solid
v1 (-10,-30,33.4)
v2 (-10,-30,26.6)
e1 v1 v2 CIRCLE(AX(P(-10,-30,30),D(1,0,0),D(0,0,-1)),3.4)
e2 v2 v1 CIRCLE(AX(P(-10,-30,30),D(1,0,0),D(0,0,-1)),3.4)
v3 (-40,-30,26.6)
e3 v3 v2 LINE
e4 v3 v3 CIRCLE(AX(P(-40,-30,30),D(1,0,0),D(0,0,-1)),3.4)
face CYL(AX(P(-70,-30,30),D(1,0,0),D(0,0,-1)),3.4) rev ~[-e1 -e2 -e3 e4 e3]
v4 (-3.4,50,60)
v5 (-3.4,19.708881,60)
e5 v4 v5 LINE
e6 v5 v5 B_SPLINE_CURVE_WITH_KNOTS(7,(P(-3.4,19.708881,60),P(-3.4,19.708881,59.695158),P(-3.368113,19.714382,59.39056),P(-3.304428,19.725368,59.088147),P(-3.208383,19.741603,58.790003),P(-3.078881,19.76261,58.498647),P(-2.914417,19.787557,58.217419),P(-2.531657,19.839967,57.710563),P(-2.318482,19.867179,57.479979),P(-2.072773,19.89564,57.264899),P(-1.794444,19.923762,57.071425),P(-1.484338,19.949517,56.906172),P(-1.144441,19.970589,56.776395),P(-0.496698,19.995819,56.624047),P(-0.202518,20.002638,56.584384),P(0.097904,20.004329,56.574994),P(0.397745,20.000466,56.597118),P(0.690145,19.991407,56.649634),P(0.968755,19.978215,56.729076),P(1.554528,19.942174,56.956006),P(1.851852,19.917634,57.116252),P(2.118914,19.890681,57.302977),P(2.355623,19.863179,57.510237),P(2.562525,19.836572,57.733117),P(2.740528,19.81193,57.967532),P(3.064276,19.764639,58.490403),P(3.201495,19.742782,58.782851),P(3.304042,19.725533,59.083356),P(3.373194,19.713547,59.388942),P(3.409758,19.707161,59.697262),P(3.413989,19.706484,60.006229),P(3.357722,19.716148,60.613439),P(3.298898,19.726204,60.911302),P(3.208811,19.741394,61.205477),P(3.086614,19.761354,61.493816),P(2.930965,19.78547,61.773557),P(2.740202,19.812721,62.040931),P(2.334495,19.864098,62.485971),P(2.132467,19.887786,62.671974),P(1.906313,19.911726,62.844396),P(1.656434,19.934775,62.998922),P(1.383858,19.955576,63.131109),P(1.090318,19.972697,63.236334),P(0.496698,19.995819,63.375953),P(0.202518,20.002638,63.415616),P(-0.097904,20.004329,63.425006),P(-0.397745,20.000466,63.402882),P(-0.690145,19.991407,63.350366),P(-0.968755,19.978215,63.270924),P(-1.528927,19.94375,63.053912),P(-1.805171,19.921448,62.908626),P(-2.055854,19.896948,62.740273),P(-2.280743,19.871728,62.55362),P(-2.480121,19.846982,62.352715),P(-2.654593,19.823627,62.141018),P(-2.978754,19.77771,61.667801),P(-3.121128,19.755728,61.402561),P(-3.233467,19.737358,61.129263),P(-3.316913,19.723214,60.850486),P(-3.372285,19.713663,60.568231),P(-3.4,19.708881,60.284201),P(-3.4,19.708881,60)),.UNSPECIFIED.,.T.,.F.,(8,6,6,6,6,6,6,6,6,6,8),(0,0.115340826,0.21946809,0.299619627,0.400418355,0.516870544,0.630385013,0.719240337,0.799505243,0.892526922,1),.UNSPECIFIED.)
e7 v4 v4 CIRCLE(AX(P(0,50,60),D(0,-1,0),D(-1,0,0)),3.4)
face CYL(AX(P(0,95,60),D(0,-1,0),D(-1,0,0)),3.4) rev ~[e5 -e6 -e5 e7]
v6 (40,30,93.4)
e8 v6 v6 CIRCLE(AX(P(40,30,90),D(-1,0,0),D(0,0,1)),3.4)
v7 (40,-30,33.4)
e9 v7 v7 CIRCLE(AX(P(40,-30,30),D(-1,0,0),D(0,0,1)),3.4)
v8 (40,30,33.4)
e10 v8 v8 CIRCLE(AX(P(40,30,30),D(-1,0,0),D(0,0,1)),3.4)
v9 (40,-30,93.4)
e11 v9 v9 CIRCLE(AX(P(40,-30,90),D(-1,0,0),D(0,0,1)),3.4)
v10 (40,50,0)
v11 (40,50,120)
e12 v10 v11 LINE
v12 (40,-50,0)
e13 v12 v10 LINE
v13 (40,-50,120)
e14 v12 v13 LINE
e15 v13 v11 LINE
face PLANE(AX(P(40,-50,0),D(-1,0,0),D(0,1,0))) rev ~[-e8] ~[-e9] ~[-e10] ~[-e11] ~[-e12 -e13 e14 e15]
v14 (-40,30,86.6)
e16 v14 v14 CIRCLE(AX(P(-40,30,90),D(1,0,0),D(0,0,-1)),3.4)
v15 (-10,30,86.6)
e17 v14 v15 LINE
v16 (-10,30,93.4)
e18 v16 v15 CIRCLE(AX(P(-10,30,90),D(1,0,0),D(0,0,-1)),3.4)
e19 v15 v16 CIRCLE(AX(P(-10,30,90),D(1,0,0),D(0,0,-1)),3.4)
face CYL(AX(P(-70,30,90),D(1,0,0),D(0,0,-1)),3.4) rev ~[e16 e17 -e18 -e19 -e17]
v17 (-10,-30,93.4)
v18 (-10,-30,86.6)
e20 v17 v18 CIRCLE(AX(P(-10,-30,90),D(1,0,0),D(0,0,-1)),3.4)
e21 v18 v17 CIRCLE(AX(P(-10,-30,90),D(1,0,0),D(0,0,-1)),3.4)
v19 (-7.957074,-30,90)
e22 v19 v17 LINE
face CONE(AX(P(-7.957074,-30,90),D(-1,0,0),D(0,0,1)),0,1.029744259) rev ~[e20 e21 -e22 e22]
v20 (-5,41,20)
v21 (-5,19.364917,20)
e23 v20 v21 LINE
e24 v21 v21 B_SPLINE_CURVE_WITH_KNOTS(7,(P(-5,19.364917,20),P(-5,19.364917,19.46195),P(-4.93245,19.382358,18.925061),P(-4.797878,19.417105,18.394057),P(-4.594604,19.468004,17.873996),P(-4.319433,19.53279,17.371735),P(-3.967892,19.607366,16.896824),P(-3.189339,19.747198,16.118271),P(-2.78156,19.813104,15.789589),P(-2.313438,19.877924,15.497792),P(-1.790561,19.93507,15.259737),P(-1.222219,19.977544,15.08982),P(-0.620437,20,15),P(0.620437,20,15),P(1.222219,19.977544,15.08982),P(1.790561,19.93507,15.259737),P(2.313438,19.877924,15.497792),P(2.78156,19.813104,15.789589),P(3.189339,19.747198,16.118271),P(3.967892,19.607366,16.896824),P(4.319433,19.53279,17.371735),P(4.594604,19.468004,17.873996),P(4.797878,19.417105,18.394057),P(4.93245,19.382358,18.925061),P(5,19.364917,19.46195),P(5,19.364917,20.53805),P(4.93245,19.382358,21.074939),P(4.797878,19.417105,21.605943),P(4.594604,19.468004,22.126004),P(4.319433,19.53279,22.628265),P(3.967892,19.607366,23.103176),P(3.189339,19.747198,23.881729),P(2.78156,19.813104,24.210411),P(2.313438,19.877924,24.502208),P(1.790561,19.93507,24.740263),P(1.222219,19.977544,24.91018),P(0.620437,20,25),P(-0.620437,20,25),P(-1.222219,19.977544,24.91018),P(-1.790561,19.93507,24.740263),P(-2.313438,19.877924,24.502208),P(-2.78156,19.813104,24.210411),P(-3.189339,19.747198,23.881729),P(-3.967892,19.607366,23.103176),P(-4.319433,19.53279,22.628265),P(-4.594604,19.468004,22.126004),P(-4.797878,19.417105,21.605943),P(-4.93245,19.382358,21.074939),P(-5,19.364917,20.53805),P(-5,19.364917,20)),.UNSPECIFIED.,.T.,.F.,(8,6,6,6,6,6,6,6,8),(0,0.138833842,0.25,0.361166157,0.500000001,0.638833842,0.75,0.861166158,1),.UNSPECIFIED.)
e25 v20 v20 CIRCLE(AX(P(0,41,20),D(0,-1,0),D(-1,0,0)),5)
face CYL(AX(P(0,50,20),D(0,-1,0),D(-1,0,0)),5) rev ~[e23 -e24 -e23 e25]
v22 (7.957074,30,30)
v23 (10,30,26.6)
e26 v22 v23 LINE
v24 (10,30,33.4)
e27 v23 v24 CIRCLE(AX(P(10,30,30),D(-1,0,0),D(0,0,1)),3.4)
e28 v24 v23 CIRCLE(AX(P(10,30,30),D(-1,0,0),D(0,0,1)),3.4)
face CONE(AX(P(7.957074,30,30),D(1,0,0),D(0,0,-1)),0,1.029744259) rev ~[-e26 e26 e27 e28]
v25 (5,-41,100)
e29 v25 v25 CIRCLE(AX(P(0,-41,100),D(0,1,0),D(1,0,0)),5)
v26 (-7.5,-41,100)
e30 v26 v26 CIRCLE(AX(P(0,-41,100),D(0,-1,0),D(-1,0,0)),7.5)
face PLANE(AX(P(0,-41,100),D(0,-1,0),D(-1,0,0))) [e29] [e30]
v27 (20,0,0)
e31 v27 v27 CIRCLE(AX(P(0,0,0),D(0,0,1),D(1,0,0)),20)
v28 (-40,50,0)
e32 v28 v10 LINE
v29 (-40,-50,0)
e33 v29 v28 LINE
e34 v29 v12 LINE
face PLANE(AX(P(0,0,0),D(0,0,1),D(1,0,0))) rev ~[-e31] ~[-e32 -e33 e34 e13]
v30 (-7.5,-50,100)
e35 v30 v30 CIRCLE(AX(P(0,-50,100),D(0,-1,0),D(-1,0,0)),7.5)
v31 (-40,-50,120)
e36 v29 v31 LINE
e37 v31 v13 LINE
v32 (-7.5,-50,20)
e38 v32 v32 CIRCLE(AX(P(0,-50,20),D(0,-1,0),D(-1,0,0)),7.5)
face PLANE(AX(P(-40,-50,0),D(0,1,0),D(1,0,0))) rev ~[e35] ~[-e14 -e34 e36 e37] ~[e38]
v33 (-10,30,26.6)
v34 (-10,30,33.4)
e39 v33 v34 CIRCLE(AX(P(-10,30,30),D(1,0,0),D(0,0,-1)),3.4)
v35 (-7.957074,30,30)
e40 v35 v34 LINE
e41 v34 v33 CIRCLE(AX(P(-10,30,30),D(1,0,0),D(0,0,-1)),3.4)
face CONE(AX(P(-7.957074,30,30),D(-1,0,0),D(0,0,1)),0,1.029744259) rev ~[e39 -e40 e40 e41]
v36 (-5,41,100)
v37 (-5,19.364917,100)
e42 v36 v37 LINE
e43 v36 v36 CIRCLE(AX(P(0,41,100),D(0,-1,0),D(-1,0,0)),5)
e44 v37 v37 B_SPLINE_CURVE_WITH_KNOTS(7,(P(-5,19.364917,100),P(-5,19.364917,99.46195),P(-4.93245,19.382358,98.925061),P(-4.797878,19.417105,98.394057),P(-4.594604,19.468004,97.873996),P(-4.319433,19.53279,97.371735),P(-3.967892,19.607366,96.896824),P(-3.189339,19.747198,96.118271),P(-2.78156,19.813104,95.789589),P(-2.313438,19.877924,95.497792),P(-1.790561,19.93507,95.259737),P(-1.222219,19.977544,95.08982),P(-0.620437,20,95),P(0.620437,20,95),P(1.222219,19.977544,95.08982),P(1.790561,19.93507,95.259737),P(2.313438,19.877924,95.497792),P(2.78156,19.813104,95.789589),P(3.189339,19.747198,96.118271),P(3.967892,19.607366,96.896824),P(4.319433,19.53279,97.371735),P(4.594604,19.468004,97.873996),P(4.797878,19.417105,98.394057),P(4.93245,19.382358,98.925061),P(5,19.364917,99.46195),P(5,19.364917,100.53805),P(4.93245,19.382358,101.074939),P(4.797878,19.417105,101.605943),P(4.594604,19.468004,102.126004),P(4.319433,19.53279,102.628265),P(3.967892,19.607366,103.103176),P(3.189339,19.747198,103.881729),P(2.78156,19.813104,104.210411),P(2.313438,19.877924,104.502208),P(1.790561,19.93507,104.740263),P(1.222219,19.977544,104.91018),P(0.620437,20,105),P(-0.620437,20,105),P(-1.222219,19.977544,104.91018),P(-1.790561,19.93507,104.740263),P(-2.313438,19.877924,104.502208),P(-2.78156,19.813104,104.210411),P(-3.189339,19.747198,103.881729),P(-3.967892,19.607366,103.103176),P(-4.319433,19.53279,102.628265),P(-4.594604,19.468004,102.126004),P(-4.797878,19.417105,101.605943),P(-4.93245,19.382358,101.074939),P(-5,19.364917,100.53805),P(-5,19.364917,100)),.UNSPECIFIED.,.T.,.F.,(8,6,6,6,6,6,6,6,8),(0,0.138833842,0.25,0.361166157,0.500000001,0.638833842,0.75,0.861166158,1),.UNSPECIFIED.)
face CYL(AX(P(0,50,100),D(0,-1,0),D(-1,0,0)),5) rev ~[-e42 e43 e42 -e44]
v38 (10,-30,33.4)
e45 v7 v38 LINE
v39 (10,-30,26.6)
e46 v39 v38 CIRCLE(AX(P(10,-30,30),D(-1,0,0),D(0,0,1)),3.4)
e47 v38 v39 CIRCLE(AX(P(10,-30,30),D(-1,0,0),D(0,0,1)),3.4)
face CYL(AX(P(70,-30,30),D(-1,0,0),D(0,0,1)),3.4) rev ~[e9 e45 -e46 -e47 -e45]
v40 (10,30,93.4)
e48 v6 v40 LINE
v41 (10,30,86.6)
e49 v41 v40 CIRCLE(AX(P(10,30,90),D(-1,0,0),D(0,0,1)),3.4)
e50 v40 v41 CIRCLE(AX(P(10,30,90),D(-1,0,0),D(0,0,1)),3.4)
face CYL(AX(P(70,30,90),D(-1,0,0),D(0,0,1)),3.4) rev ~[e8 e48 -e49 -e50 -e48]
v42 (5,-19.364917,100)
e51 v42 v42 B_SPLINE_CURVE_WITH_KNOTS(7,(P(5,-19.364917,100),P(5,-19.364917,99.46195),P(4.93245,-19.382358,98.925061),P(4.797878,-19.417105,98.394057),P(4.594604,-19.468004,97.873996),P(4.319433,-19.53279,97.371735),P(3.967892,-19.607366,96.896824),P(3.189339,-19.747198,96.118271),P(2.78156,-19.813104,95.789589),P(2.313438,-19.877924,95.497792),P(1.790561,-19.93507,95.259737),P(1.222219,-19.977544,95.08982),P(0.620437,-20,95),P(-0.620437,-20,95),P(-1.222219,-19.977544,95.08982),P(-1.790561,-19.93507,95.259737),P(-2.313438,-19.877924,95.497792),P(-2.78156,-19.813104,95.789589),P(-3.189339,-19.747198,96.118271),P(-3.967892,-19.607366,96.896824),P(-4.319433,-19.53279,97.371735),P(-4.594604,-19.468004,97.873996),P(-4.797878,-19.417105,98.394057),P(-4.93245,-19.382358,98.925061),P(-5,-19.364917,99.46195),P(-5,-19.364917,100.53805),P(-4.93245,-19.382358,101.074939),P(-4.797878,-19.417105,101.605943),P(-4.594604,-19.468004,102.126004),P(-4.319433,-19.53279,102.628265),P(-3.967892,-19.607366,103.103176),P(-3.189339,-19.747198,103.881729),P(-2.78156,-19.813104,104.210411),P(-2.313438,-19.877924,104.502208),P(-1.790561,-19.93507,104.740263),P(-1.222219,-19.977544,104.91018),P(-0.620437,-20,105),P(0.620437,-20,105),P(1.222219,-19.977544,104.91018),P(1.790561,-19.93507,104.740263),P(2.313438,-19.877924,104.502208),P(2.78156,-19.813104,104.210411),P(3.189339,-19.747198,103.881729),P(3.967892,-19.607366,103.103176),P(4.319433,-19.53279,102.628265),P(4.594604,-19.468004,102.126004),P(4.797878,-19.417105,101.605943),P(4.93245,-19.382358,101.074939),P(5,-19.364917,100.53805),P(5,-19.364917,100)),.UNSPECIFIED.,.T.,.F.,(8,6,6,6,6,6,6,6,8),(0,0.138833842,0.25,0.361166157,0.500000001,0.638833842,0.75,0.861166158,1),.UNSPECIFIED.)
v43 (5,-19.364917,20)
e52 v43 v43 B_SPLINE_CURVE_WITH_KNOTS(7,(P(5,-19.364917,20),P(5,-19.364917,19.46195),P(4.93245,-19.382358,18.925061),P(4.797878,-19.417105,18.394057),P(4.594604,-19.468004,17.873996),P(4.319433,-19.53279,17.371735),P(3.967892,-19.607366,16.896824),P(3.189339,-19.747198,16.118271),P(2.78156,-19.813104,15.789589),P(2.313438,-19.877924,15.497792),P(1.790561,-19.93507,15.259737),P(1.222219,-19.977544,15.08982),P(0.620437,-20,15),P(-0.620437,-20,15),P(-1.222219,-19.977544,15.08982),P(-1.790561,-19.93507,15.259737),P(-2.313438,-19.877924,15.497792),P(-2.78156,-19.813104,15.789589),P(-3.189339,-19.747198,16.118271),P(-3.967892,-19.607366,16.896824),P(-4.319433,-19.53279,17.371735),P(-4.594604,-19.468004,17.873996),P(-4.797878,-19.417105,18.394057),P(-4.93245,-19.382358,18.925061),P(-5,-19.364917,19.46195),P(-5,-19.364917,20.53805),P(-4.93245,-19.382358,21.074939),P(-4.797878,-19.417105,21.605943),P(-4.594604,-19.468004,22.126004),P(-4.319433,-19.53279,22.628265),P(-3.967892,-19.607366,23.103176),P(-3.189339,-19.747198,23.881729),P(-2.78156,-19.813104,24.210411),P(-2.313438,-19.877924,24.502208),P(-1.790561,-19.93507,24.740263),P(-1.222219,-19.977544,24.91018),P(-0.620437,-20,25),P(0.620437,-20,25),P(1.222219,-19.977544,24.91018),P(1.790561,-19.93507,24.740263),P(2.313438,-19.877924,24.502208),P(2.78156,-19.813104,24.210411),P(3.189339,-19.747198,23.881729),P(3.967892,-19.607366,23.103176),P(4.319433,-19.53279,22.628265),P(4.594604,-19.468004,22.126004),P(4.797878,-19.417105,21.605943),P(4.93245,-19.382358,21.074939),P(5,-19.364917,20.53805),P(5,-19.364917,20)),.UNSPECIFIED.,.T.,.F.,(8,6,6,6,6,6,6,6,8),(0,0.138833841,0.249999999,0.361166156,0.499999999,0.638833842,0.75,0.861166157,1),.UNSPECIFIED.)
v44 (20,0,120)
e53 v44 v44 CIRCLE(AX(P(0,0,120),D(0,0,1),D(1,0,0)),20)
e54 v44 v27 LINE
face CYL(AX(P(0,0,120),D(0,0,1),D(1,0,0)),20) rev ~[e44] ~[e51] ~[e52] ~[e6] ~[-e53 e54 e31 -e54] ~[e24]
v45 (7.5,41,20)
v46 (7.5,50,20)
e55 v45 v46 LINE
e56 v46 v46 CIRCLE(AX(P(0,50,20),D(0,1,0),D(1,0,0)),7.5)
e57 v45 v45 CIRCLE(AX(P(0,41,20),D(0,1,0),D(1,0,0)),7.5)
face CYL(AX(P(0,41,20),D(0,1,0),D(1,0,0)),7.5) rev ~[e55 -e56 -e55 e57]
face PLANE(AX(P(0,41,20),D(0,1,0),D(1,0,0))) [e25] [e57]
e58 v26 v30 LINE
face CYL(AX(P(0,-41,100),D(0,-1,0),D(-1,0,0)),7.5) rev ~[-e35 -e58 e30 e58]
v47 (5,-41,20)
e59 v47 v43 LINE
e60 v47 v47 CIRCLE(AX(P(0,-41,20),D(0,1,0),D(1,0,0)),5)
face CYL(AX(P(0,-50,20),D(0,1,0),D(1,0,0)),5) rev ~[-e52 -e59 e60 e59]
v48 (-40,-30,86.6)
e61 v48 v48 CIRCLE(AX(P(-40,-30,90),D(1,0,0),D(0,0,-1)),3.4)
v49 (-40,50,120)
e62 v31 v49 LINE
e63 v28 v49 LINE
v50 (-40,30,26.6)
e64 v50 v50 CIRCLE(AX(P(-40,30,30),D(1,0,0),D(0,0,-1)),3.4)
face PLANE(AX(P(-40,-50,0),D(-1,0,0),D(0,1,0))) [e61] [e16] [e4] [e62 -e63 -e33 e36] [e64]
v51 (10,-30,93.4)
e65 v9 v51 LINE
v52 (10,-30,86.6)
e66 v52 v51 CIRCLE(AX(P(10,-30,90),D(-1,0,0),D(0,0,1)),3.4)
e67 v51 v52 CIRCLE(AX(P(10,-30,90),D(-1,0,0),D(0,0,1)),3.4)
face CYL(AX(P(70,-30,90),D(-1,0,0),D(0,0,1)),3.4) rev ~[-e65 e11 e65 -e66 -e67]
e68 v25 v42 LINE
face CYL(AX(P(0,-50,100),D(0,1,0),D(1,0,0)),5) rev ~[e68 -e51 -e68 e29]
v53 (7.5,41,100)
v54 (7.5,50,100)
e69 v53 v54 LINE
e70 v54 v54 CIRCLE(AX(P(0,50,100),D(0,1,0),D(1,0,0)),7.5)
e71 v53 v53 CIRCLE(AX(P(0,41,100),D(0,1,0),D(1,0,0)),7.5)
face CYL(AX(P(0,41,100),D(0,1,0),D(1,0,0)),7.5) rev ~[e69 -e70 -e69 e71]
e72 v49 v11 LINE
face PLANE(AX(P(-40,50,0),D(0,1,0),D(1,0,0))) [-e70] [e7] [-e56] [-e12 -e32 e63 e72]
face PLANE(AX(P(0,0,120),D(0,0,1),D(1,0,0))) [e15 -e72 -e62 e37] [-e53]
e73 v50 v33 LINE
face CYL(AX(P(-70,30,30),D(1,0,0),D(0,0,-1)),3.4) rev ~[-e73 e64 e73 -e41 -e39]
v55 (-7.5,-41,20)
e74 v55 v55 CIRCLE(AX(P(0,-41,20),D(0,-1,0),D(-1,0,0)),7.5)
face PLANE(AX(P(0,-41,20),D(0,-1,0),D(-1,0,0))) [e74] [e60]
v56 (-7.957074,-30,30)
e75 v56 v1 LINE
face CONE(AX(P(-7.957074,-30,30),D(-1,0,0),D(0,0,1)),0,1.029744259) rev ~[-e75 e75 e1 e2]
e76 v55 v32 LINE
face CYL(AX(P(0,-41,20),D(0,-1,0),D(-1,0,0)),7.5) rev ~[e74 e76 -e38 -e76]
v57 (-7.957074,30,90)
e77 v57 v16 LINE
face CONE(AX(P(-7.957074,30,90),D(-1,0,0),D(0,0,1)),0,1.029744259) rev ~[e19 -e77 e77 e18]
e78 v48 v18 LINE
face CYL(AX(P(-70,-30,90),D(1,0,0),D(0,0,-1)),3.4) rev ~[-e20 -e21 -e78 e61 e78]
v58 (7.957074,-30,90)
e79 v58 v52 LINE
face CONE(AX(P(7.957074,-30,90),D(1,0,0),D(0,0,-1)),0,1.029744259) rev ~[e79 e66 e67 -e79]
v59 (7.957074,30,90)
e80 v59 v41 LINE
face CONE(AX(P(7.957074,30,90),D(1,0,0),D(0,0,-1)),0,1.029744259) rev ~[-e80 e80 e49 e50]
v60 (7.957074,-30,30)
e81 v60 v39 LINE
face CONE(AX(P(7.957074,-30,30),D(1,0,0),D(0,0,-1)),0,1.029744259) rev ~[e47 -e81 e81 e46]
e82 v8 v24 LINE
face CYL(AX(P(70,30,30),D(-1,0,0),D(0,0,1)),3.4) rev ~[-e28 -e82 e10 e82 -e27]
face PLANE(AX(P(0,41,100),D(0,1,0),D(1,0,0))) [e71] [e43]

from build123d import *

# Parameters (mm, degrees)
SKETCH1_W                                          = 80
SKETCH1_H                                          = 100
BOSS_EXTRUDE1_DEPTH                                = 120
SKETCH2_R                                          = 20
CUT_EXTRUDE1_DEPTH                                 = 137.014705087
HOLE_SIZE_BASED_ON_HEX_SOCKET_CAP_SCRE_D           = 10
HOLE_SIZE_BASED_ON_HEX_SOCKET_CAP_SCRE_DEPTH       = 35
HOLE_SIZE_BASED_ON_HEX_SOCKET_CAP_SCRE_CBORE_D     = 15
HOLE_SIZE_BASED_ON_HEX_SOCKET_CAP_SCRE_CBORE_DEPTH = 9
HOLE_SIZE_BASED_ON_HEX_SOCKET_CAP_SCRE_TIP         = 3.004303095
HOLE_WIZARD_2_D                                    = 10
HOLE_WIZARD_2_DEPTH                                = 50
HOLE_WIZARD_2_CBORE_D                              = 15
HOLE_WIZARD_2_CBORE_DEPTH                          = 9
HOLE_WIZARD_2_TIP                                  = 3.004303095
M8_TAPPED_HOLE1_D                                  = 6.8
M8_TAPPED_HOLE1_DEPTH                              = 30
M8_TAPPED_HOLE1_TIP                                = 2.042926105
M8_TAPPED_HOLE2_D                                  = 6.8
M8_TAPPED_HOLE2_DEPTH                              = 30
M8_TAPPED_HOLE2_TIP                                = 2.042926105
M8_TAPPED_HOLE3_D                                  = 6.8
M8_TAPPED_HOLE3_DEPTH                              = 45
M8_TAPPED_HOLE3_TIP                                = 2.042926105


with BuildPart() as part:
    # Sketch1 → Boss-Extrude1 (new body)
    with BuildSketch(Plane.XY):
        Rectangle(SKETCH1_W, SKETCH1_H)
    extrude(amount=BOSS_EXTRUDE1_DEPTH)

    # Sketch2 → Cut-Extrude1 (cut, through all)
    with BuildSketch(Plane.XY.offset(120)):
        Circle(SKETCH2_R)
    extrude(amount=-CUT_EXTRUDE1_DEPTH, mode=Mode.SUBTRACT)

    # Hole Size (based on) hex socket cap screw type 2
    with Locations(Plane(origin=(0, 50, 0), x_dir=(1, 0, 0), z_dir=(0, 1, 0))):
        with Locations((0, -20), (0, -100)):
            CounterBoreHole(HOLE_SIZE_BASED_ON_HEX_SOCKET_CAP_SCRE_D / 2, HOLE_SIZE_BASED_ON_HEX_SOCKET_CAP_SCRE_CBORE_D / 2, HOLE_SIZE_BASED_ON_HEX_SOCKET_CAP_SCRE_CBORE_DEPTH, depth=HOLE_SIZE_BASED_ON_HEX_SOCKET_CAP_SCRE_DEPTH)
            with Locations((0, 0, -(HOLE_SIZE_BASED_ON_HEX_SOCKET_CAP_SCRE_DEPTH + HOLE_SIZE_BASED_ON_HEX_SOCKET_CAP_SCRE_TIP / 2))):  # 118° drill point
                Cone(0, HOLE_SIZE_BASED_ON_HEX_SOCKET_CAP_SCRE_D / 2, HOLE_SIZE_BASED_ON_HEX_SOCKET_CAP_SCRE_TIP, mode=Mode.SUBTRACT)

    # 打孔尺寸(%根据)内六角圆柱头螺钉的类型2
    with Locations(Plane(origin=(0, -50, 0), x_dir=(-1, 0, 0), z_dir=(0, -1, 0))):
        with Locations((0, -20), (0, -100)):
            CounterBoreHole(HOLE_WIZARD_2_D / 2, HOLE_WIZARD_2_CBORE_D / 2, HOLE_WIZARD_2_CBORE_DEPTH, depth=HOLE_WIZARD_2_DEPTH)
            with Locations((0, 0, -(HOLE_WIZARD_2_DEPTH + HOLE_WIZARD_2_TIP / 2))):  # 118° drill point
                Cone(0, HOLE_WIZARD_2_D / 2, HOLE_WIZARD_2_TIP, mode=Mode.SUBTRACT)

    # M8 Tapped Hole1
    with Locations(Plane.ZY.offset(40)):
        with Locations((30, 30), (90, 30), (90, -30), (30, -30)):
            Hole(M8_TAPPED_HOLE1_D / 2, depth=M8_TAPPED_HOLE1_DEPTH)
            with Locations((0, 0, -(M8_TAPPED_HOLE1_DEPTH + M8_TAPPED_HOLE1_TIP / 2))):  # 118° drill point
                Cone(0, M8_TAPPED_HOLE1_D / 2, M8_TAPPED_HOLE1_TIP, mode=Mode.SUBTRACT)

    # M8 Tapped Hole2
    with Locations(Plane(origin=(40, 0, 0), x_dir=(0, 0, -1), z_dir=(1, 0, 0))):
        with Locations((-90, 30), (-30, 30), (-30, -30), (-90, -30)):
            Hole(M8_TAPPED_HOLE2_D / 2, depth=M8_TAPPED_HOLE2_DEPTH)
            with Locations((0, 0, -(M8_TAPPED_HOLE2_DEPTH + M8_TAPPED_HOLE2_TIP / 2))):  # 118° drill point
                Cone(0, M8_TAPPED_HOLE2_D / 2, M8_TAPPED_HOLE2_TIP, mode=Mode.SUBTRACT)

    # M8 Tapped Hole3
    with Locations(Plane(origin=(0, 50, 0), x_dir=(1, 0, 0), z_dir=(0, 1, 0))):
        with Locations((0, -60)):
            Hole(M8_TAPPED_HOLE3_D / 2, depth=M8_TAPPED_HOLE3_DEPTH)
            with Locations((0, 0, -(M8_TAPPED_HOLE3_DEPTH + M8_TAPPED_HOLE3_TIP / 2))):  # 118° drill point
                Cone(0, M8_TAPPED_HOLE3_D / 2, M8_TAPPED_HOLE3_TIP, mode=Mode.SUBTRACT)


solid = part.part
